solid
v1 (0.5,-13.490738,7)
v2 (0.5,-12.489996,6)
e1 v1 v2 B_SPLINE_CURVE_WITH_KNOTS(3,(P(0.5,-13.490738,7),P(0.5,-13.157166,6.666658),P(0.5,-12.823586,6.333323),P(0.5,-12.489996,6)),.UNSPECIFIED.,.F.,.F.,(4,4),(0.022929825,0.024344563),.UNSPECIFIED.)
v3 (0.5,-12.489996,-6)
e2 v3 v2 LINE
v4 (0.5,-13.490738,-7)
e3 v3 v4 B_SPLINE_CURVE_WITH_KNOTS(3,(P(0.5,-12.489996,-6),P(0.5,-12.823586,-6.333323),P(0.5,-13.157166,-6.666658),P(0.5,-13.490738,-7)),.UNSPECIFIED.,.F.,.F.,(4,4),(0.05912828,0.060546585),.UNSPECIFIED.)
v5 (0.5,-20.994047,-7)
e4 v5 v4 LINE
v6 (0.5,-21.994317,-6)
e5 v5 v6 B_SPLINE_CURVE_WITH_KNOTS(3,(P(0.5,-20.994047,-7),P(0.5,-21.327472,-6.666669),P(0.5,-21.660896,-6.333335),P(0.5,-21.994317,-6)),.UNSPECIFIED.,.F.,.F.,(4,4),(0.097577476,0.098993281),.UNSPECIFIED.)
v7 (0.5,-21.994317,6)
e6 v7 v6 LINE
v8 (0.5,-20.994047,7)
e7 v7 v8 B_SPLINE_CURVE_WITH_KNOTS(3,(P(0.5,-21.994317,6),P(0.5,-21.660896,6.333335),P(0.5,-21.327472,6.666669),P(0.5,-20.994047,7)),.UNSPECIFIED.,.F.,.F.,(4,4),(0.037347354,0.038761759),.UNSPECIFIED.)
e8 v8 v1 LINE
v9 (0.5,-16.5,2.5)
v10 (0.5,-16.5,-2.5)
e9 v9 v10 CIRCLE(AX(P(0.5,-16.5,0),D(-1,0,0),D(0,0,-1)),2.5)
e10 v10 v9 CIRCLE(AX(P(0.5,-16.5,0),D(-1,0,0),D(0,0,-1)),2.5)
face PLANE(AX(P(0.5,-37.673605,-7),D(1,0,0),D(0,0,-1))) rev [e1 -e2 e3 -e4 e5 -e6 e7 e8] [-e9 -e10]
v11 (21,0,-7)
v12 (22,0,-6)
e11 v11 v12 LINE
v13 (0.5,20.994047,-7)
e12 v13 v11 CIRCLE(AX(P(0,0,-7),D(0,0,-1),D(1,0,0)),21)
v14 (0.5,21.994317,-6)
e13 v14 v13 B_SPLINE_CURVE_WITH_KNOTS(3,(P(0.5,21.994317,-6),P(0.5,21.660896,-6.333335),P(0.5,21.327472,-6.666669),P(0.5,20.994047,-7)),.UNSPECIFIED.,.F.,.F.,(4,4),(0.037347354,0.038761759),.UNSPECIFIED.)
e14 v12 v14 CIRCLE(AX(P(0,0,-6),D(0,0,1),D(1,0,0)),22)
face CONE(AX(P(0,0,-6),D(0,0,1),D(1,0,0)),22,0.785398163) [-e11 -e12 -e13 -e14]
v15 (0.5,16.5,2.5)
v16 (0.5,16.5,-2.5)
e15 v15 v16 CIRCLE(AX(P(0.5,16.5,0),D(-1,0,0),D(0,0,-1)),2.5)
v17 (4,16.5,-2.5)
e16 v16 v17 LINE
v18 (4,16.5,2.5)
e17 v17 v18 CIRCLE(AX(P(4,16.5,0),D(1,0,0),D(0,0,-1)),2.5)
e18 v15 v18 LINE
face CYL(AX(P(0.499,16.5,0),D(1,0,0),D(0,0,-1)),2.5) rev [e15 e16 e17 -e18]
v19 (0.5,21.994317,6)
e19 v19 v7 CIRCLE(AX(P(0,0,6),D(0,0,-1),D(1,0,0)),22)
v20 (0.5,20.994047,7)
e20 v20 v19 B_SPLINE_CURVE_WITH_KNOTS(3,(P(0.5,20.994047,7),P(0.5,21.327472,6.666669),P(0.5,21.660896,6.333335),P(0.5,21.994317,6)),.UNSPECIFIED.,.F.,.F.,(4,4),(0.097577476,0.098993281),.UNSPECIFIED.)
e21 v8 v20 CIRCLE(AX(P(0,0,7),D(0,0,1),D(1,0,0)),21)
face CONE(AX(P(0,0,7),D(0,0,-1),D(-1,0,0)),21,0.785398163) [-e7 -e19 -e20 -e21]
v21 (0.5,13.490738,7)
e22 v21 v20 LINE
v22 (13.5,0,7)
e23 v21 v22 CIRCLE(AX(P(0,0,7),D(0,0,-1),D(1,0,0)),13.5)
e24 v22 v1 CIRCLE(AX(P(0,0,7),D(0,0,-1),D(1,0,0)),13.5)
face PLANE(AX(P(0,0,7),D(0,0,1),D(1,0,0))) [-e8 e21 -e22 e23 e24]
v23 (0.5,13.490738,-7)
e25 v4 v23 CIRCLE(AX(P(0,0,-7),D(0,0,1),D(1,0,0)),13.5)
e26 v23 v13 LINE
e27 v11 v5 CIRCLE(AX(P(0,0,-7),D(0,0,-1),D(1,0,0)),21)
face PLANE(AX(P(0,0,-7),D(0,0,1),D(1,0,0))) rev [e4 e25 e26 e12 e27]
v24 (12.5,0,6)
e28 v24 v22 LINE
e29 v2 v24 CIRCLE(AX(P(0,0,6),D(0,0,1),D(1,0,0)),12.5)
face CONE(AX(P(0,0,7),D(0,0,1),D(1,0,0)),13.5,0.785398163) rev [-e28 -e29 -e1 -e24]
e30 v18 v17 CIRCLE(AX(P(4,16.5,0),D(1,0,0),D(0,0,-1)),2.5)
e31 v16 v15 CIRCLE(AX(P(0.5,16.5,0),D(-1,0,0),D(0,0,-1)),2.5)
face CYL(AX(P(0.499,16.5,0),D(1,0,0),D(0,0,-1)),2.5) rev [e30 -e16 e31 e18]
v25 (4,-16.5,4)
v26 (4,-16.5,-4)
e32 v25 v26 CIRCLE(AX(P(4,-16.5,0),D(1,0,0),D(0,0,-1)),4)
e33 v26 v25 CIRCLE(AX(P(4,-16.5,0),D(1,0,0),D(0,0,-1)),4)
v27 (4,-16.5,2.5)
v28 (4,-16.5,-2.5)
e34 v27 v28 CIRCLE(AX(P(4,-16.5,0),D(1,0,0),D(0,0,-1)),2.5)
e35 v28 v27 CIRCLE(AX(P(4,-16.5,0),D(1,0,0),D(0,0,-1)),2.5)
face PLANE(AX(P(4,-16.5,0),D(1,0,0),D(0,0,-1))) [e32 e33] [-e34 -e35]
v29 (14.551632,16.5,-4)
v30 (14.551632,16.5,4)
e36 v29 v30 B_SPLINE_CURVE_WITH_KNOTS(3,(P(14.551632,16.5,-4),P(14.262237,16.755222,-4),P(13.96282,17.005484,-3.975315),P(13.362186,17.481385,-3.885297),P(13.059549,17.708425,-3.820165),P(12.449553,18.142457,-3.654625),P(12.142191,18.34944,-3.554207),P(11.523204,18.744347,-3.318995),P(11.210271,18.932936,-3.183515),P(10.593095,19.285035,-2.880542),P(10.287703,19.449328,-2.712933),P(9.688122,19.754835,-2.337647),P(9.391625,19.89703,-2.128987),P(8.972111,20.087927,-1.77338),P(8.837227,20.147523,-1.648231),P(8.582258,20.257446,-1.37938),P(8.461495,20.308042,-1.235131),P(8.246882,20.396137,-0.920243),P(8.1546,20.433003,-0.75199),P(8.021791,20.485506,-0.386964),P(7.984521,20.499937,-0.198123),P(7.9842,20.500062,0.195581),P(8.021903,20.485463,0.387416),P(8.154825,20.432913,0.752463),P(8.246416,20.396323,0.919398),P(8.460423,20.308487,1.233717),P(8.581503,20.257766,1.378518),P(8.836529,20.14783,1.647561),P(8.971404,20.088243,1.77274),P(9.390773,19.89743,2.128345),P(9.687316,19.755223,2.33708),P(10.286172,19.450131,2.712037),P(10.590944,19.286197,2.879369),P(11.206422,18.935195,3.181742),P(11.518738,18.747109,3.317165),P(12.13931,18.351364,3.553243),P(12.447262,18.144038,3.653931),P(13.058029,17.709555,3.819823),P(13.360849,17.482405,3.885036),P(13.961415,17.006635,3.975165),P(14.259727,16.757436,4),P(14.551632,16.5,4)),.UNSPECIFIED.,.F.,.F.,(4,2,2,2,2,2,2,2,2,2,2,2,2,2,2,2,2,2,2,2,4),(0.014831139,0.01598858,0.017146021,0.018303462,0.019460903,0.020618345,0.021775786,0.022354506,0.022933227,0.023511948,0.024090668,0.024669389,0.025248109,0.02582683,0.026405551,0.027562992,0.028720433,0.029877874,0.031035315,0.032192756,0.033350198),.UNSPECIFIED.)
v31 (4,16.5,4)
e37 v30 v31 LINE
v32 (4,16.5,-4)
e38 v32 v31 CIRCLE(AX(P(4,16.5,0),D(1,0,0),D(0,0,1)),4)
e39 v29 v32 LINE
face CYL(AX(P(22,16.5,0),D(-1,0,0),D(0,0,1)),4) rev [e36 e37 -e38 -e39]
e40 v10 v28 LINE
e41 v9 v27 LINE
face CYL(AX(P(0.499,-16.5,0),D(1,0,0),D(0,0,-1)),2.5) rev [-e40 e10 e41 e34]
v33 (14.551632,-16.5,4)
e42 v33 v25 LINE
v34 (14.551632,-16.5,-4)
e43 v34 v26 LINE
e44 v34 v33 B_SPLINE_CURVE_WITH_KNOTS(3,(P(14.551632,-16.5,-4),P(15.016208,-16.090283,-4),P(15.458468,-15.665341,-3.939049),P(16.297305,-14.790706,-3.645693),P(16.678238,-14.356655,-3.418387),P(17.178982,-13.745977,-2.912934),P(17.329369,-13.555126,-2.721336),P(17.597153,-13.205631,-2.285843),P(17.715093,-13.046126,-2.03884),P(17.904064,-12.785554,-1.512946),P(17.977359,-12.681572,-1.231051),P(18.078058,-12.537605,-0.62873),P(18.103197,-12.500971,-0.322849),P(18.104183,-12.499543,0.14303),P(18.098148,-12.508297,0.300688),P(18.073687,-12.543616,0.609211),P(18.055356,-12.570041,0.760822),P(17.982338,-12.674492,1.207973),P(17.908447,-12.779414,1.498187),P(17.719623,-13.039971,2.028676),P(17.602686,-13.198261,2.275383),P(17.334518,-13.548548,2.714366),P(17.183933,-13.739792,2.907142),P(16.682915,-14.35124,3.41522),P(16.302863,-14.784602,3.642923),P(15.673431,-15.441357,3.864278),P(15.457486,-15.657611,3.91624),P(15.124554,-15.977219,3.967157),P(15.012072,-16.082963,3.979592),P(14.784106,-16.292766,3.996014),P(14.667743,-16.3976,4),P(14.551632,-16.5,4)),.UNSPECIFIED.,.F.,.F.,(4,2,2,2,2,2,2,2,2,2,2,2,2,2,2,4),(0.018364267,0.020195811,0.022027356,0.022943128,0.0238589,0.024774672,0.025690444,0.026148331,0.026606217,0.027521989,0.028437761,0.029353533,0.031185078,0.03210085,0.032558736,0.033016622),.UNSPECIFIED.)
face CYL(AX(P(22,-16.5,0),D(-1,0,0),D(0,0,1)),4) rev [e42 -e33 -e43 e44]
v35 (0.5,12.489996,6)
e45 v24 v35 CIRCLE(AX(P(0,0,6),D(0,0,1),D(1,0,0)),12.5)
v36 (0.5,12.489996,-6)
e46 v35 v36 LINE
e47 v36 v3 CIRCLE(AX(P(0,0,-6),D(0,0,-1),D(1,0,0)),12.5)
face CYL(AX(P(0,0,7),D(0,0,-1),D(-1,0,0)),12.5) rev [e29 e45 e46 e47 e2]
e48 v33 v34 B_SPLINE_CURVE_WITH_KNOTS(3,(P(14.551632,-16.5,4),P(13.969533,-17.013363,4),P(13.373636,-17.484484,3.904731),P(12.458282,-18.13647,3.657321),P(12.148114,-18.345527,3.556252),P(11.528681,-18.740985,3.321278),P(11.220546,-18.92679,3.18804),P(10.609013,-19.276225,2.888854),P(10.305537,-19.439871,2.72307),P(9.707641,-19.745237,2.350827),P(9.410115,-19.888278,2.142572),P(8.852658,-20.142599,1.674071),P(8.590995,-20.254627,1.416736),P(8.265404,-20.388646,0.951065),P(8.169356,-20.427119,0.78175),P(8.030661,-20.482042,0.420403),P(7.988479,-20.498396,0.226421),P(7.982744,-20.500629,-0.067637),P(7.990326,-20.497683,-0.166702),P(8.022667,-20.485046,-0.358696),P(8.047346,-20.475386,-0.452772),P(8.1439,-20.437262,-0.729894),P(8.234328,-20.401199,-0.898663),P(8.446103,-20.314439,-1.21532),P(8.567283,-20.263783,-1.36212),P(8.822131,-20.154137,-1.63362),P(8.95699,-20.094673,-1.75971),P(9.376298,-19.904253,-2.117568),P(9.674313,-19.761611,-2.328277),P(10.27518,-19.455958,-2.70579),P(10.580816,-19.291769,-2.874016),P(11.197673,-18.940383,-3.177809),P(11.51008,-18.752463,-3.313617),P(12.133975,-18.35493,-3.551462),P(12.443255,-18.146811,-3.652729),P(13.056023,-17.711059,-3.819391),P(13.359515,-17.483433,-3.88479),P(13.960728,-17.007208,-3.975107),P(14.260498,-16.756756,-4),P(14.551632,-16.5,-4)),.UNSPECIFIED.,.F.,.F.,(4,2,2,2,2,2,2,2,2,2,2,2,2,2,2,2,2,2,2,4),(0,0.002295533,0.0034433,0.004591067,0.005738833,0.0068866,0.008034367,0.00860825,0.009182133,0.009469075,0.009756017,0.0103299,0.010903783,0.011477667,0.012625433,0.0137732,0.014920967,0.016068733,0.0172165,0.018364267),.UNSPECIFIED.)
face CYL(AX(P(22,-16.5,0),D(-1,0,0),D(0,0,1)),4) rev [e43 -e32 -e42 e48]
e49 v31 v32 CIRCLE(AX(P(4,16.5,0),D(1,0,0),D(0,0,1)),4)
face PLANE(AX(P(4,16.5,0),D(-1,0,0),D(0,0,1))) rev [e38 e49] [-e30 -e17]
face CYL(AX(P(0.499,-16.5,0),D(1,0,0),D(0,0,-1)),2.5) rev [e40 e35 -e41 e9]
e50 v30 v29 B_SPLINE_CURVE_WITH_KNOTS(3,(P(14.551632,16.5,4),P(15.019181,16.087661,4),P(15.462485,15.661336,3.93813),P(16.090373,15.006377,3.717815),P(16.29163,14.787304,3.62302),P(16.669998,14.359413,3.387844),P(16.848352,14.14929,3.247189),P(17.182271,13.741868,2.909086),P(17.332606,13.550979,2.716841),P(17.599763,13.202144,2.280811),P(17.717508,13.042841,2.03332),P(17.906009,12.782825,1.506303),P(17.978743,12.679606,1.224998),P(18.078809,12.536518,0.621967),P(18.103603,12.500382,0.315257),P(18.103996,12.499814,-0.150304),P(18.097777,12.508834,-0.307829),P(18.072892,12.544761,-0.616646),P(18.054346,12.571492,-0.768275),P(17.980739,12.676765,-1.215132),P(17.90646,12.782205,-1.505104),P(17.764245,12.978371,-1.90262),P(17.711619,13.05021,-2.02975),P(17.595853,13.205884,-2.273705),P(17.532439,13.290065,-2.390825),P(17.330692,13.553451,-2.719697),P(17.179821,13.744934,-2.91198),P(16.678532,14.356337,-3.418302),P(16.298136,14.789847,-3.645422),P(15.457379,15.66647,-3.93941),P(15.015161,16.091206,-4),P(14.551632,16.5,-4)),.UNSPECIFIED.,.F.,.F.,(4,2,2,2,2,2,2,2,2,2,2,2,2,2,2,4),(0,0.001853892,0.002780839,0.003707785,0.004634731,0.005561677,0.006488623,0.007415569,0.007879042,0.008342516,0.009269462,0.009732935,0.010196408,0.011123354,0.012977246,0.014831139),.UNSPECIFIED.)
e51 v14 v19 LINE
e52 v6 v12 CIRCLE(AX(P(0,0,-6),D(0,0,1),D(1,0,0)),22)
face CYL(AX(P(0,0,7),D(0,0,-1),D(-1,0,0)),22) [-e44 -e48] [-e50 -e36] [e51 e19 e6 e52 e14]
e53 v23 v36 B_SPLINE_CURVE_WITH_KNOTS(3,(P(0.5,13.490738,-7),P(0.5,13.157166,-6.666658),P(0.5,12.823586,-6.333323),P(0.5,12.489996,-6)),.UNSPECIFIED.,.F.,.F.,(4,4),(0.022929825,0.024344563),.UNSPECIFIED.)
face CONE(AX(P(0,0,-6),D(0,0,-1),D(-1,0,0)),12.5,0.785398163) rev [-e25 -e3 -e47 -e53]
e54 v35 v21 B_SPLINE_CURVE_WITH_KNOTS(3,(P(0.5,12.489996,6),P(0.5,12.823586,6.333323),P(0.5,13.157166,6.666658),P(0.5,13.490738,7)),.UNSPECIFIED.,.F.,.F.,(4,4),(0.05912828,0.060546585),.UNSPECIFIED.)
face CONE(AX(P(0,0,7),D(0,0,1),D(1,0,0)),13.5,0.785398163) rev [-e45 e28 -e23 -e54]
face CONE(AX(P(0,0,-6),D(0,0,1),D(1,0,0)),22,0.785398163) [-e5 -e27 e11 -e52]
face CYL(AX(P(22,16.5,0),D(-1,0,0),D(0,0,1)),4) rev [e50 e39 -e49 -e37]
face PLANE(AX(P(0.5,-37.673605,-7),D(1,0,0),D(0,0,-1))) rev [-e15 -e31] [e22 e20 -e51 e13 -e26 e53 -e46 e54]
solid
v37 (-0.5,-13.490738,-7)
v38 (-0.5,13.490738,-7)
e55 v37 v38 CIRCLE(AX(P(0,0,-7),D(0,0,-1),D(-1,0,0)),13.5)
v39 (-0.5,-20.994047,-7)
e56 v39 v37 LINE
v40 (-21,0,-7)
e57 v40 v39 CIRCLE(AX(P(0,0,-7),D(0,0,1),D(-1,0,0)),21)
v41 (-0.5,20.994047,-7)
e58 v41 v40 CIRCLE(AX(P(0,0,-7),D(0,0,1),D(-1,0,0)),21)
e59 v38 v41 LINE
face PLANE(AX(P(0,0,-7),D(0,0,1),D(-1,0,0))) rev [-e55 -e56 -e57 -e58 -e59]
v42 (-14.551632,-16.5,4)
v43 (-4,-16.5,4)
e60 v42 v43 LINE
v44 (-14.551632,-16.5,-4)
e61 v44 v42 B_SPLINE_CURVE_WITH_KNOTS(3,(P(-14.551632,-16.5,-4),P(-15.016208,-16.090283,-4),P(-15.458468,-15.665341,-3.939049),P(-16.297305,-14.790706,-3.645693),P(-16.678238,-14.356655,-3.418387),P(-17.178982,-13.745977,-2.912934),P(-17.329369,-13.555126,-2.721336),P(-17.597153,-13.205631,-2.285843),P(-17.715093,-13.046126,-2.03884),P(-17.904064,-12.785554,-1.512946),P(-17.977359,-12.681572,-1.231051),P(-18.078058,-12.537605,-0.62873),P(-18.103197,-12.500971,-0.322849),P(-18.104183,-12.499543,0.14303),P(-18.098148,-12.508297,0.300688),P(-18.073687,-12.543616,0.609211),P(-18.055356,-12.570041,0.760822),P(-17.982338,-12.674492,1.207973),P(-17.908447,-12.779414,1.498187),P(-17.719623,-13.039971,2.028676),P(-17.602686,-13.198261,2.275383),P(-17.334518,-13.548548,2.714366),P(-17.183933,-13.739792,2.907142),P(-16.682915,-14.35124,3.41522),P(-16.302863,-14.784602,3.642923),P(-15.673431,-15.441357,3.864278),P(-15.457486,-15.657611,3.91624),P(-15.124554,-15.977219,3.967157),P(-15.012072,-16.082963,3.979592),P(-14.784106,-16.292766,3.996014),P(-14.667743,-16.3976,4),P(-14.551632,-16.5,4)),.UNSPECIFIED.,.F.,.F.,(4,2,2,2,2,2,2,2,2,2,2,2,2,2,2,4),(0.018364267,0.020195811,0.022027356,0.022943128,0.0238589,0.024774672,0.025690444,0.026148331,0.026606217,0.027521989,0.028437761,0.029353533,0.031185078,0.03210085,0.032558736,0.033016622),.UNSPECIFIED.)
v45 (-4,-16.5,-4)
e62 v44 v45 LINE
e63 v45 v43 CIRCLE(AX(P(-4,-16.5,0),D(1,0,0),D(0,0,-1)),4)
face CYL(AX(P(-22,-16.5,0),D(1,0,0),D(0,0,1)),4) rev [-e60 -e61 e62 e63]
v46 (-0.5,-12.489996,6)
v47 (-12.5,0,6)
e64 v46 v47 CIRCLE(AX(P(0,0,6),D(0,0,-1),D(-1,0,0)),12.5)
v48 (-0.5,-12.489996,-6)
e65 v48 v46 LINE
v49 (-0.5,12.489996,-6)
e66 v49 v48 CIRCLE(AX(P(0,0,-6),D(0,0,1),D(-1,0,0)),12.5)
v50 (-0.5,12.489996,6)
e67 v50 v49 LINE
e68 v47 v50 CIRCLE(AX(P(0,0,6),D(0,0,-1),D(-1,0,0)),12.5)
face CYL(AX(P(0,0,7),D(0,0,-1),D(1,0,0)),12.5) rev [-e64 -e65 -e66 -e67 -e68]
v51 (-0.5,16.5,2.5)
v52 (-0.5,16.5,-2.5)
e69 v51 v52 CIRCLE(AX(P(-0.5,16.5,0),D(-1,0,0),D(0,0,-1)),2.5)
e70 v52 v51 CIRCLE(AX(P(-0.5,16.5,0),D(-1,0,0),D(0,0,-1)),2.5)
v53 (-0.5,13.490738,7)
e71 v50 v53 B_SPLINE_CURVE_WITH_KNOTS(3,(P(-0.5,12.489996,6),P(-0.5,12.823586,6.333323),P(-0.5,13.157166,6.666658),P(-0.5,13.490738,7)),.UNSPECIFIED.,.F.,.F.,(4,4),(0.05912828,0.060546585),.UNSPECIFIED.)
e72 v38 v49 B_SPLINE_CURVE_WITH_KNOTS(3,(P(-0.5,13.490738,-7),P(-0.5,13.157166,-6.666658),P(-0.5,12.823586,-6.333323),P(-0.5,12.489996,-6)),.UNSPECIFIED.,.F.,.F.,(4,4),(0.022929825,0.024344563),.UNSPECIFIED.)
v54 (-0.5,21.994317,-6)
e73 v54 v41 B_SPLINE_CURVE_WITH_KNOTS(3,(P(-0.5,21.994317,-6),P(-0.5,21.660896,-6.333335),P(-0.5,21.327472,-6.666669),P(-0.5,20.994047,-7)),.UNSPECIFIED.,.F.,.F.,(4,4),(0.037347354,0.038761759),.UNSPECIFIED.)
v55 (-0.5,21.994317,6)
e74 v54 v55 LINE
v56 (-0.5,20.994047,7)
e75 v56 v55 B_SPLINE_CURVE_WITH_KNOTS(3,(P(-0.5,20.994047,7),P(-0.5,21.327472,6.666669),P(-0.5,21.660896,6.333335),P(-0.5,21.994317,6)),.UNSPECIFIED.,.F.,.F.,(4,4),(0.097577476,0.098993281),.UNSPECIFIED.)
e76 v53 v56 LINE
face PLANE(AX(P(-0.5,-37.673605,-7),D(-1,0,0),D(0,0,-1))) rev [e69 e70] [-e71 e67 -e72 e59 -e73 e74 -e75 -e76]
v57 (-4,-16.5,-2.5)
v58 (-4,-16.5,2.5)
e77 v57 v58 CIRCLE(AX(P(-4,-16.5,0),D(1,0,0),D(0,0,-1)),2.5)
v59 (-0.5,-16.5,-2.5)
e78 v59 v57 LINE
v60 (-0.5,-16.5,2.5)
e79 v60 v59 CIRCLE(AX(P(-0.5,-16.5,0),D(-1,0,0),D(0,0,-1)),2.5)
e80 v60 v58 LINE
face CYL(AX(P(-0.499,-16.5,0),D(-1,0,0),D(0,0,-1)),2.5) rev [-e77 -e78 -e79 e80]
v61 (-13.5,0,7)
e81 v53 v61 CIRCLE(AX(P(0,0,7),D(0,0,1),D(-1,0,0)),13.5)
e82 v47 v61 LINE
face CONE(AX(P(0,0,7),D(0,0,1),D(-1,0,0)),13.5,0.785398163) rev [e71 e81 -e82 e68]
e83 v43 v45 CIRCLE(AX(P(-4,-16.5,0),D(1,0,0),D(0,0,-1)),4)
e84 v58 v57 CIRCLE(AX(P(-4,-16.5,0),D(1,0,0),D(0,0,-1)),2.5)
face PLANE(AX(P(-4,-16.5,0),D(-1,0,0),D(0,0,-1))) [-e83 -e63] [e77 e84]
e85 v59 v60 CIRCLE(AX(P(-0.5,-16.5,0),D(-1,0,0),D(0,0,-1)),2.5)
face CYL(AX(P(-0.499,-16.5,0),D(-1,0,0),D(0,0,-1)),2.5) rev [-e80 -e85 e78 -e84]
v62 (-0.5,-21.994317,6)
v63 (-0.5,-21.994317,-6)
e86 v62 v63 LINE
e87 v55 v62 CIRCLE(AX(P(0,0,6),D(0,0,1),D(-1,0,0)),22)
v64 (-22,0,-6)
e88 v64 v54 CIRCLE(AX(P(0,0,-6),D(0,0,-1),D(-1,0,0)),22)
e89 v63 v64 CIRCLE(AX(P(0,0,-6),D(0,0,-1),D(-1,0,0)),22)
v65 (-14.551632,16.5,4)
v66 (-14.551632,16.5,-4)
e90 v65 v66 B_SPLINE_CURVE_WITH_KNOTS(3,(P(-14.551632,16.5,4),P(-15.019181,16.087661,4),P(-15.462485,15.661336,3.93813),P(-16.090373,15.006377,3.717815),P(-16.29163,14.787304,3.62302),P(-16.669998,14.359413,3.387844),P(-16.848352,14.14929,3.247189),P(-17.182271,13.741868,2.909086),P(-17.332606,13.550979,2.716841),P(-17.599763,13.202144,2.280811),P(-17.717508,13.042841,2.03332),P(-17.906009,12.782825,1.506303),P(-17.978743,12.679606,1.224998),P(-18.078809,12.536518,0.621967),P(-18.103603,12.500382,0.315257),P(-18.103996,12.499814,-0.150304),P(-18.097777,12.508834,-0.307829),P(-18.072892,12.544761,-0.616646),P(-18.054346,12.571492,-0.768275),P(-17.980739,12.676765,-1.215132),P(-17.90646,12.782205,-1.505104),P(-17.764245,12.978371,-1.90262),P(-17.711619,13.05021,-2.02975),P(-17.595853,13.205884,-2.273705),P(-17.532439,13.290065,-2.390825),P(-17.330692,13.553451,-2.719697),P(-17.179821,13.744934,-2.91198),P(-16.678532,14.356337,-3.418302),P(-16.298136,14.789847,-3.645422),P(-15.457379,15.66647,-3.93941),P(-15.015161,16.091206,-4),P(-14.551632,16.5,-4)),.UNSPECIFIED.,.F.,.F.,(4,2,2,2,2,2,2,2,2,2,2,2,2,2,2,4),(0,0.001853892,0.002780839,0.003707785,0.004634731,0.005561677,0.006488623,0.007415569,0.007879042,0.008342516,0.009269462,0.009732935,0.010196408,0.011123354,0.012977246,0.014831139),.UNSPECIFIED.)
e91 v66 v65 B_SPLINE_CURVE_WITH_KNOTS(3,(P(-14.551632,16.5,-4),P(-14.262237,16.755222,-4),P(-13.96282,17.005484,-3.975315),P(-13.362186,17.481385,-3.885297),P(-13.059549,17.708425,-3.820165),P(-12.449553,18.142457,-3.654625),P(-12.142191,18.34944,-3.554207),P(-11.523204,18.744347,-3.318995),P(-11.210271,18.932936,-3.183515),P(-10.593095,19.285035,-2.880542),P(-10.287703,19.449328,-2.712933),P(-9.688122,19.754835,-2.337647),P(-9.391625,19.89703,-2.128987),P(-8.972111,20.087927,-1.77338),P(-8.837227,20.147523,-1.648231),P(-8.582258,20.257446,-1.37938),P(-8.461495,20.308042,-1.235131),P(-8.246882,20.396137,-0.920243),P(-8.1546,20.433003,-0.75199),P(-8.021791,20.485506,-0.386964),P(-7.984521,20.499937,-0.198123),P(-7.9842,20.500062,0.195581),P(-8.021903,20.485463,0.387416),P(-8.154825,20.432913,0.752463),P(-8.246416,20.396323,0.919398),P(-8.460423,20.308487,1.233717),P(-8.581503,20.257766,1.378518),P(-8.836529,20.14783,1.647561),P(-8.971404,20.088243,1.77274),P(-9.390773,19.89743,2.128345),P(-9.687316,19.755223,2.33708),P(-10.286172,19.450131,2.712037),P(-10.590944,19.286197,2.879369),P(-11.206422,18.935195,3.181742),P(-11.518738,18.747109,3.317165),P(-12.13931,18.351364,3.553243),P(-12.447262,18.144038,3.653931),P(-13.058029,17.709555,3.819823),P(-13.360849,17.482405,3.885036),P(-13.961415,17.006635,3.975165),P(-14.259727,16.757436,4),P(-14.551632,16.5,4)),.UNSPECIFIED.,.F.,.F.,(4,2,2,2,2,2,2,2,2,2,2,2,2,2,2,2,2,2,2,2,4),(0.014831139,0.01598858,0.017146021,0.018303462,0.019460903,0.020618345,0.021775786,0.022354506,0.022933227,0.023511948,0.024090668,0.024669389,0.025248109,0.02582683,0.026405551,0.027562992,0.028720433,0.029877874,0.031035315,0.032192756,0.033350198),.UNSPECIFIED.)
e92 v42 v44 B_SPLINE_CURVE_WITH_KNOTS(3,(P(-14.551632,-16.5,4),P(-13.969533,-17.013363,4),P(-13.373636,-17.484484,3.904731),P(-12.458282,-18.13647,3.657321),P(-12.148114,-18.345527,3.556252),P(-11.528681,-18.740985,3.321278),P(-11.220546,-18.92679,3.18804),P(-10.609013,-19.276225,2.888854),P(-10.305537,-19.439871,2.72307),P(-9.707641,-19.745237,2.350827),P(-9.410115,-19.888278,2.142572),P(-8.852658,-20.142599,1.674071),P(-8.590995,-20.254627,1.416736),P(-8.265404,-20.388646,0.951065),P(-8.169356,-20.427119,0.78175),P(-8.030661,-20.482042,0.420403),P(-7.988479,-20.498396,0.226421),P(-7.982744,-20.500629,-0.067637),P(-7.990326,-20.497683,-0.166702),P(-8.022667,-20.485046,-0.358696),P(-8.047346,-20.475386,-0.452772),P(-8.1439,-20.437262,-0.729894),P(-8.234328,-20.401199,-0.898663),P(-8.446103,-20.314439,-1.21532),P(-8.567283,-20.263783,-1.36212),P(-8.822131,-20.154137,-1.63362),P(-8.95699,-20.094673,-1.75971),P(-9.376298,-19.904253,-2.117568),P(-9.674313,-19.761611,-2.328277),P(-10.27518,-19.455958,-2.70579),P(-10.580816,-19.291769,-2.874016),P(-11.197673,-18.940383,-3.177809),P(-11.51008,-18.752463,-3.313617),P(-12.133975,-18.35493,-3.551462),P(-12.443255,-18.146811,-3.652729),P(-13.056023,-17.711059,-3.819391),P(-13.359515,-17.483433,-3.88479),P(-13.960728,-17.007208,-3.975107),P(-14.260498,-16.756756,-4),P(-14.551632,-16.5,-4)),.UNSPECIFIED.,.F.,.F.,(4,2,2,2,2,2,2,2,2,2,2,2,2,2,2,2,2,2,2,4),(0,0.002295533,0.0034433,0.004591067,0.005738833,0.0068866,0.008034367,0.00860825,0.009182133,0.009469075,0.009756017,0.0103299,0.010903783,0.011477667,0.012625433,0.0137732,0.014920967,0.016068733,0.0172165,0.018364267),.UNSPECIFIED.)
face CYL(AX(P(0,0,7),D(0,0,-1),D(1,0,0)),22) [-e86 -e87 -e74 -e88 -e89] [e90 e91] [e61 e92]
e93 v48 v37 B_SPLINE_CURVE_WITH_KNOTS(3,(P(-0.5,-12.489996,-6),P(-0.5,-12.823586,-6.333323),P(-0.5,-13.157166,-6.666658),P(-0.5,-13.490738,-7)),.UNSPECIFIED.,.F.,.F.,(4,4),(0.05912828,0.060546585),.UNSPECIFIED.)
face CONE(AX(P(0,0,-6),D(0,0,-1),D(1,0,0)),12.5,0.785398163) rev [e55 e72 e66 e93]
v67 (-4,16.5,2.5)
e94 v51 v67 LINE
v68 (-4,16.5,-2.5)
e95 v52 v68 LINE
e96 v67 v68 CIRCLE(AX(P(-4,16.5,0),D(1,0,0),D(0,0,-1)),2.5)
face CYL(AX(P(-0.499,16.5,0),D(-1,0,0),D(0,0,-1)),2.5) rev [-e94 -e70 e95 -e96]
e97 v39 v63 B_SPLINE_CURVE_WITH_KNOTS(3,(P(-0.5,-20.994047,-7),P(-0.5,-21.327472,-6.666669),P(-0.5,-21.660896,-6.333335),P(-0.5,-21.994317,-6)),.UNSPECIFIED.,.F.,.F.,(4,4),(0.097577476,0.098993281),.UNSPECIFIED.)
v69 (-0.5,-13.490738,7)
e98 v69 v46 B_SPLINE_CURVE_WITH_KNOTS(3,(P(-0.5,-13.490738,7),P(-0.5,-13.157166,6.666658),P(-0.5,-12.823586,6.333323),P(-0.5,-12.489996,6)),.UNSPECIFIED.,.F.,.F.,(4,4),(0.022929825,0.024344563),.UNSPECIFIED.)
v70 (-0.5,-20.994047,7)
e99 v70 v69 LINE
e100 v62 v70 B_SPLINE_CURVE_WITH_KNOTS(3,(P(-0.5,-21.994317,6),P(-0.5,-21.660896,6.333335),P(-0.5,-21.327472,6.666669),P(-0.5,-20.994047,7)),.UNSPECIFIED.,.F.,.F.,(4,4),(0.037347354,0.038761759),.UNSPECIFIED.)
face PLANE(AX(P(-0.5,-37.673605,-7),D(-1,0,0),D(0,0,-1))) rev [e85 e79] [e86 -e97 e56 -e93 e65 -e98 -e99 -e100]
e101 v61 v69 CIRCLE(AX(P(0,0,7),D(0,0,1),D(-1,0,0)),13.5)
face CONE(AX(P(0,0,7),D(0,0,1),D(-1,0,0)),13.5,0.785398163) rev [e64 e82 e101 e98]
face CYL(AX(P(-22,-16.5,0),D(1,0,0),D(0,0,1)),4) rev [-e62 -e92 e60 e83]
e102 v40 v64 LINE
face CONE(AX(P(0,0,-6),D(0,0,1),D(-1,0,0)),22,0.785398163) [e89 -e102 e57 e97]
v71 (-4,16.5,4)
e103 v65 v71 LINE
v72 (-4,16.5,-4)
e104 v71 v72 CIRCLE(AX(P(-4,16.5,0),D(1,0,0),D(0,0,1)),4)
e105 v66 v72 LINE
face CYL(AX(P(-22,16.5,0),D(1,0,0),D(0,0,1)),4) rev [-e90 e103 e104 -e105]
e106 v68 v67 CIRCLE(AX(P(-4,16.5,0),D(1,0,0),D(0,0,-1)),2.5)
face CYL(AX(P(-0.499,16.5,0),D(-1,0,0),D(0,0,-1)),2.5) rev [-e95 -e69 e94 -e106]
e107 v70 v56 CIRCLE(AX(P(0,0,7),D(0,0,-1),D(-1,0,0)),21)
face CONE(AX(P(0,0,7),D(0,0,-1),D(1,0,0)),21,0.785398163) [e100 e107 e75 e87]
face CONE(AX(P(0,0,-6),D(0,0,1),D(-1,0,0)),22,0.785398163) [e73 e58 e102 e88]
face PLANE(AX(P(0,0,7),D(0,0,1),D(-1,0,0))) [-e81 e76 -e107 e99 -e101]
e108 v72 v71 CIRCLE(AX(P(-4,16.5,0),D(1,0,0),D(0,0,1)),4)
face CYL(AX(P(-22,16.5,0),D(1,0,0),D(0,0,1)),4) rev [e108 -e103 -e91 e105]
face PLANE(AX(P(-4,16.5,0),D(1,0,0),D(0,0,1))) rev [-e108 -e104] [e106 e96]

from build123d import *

# Parameters (mm, degrees)
EXTRUDE_1_DEPTH     = 7
CHAMFER_1_SIZE      = 1
SKETCH_2_W          = 1
SKETCH_2_H          = 75.347210032
CUT_EXTRUDE_1_DEPTH = 35.117444218
SKETCH_3_R          = 4
CUT_EXTRUDE_2_DEPTH = 30.270292107
CUT_EXTRUDE_3_REACH = 31.27
SKETCH_4_R          = 2.5


with BuildPart() as part:
    # 草图1 → 凸台-拉伸1 (new, symmetric)
    with BuildSketch(Plane.XY):
        with BuildLine():
            Line((0, 22), (0, 12.5))
            ThreePointArc((0, 12.5), (12.5, 0), (0, -12.5))
            Line((0, -12.5), (0, -22))
            ThreePointArc((0, -22), (22, 0), (0, 22))
        make_face()
    extrude(amount=EXTRUDE_1_DEPTH, both=True)

    # 倒角1
    chamfer_1_edges = [part.edges().sort_by_distance(p)[0] for p in [
        (12.5, 0, 7),
        (22, 0, 7),
        (12.5, 0, -7),
        (22, 0, -7),
    ]]
    chamfer(chamfer_1_edges, length=CHAMFER_1_SIZE)

    # 草图2 → 切除-拉伸1 (cut, through all)
    with BuildSketch(Plane.XY.offset(7)):
        Rectangle(SKETCH_2_W, SKETCH_2_H)
    extrude(amount=-CUT_EXTRUDE_1_DEPTH, mode=Mode.SUBTRACT)

    # 草图3 → 切除-拉伸2 (cut, through all)
    with BuildSketch(Plane(origin=(4, 0, 0), x_dir=(0, 0, -1), z_dir=(1, 0, 0))):
        with Locations(Location((0, -16.5, 0), (0, 0, 180))):
            Circle(SKETCH_3_R)
        with Locations(Location((0, 16.5, 0), (0, 0, 180))):
            Circle(SKETCH_3_R)
    extrude(amount=CUT_EXTRUDE_2_DEPTH, mode=Mode.SUBTRACT)

    # 草图4 → 切除-拉伸3 (cut, up to next)
    with BuildSketch(Plane(origin=(4, 0, 0), x_dir=(0, 0, -1), z_dir=(1, 0, 0)), mode=Mode.PRIVATE) as cut_extrude_3_sk1:
        with Locations((0, 16.5)):
            Circle(SKETCH_4_R)
    cut_extrude_3_tool1 = extrude(cut_extrude_3_sk1.sketch, amount=-CUT_EXTRUDE_3_REACH, mode=Mode.PRIVATE) & part.part
    # 草图4 → 切除-拉伸3 (cut, up to next)
    with BuildSketch(Plane(origin=(4, 0, 0), x_dir=(0, 0, -1), z_dir=(1, 0, 0)), mode=Mode.PRIVATE) as cut_extrude_3_sk2:
        with Locations((0, -16.5)):
            Circle(SKETCH_4_R)
    cut_extrude_3_tool2 = extrude(cut_extrude_3_sk2.sketch, amount=-CUT_EXTRUDE_3_REACH, mode=Mode.PRIVATE) & part.part
    add(cut_extrude_3_tool1.solids().sort_by_distance((4, 16.5, 0))[0], mode=Mode.SUBTRACT)
    add(cut_extrude_3_tool2.solids().sort_by_distance((4, -16.5, 0))[0], mode=Mode.SUBTRACT)


with BuildPart() as body_2:
    # 镜向5: mirrored copy
    add(part.part.mirror(Plane(origin=(0, 0, 0), x_dir=(0, 0, 1), z_dir=(1, 0, 0))))


solid = Compound([part.part, body_2.part])
